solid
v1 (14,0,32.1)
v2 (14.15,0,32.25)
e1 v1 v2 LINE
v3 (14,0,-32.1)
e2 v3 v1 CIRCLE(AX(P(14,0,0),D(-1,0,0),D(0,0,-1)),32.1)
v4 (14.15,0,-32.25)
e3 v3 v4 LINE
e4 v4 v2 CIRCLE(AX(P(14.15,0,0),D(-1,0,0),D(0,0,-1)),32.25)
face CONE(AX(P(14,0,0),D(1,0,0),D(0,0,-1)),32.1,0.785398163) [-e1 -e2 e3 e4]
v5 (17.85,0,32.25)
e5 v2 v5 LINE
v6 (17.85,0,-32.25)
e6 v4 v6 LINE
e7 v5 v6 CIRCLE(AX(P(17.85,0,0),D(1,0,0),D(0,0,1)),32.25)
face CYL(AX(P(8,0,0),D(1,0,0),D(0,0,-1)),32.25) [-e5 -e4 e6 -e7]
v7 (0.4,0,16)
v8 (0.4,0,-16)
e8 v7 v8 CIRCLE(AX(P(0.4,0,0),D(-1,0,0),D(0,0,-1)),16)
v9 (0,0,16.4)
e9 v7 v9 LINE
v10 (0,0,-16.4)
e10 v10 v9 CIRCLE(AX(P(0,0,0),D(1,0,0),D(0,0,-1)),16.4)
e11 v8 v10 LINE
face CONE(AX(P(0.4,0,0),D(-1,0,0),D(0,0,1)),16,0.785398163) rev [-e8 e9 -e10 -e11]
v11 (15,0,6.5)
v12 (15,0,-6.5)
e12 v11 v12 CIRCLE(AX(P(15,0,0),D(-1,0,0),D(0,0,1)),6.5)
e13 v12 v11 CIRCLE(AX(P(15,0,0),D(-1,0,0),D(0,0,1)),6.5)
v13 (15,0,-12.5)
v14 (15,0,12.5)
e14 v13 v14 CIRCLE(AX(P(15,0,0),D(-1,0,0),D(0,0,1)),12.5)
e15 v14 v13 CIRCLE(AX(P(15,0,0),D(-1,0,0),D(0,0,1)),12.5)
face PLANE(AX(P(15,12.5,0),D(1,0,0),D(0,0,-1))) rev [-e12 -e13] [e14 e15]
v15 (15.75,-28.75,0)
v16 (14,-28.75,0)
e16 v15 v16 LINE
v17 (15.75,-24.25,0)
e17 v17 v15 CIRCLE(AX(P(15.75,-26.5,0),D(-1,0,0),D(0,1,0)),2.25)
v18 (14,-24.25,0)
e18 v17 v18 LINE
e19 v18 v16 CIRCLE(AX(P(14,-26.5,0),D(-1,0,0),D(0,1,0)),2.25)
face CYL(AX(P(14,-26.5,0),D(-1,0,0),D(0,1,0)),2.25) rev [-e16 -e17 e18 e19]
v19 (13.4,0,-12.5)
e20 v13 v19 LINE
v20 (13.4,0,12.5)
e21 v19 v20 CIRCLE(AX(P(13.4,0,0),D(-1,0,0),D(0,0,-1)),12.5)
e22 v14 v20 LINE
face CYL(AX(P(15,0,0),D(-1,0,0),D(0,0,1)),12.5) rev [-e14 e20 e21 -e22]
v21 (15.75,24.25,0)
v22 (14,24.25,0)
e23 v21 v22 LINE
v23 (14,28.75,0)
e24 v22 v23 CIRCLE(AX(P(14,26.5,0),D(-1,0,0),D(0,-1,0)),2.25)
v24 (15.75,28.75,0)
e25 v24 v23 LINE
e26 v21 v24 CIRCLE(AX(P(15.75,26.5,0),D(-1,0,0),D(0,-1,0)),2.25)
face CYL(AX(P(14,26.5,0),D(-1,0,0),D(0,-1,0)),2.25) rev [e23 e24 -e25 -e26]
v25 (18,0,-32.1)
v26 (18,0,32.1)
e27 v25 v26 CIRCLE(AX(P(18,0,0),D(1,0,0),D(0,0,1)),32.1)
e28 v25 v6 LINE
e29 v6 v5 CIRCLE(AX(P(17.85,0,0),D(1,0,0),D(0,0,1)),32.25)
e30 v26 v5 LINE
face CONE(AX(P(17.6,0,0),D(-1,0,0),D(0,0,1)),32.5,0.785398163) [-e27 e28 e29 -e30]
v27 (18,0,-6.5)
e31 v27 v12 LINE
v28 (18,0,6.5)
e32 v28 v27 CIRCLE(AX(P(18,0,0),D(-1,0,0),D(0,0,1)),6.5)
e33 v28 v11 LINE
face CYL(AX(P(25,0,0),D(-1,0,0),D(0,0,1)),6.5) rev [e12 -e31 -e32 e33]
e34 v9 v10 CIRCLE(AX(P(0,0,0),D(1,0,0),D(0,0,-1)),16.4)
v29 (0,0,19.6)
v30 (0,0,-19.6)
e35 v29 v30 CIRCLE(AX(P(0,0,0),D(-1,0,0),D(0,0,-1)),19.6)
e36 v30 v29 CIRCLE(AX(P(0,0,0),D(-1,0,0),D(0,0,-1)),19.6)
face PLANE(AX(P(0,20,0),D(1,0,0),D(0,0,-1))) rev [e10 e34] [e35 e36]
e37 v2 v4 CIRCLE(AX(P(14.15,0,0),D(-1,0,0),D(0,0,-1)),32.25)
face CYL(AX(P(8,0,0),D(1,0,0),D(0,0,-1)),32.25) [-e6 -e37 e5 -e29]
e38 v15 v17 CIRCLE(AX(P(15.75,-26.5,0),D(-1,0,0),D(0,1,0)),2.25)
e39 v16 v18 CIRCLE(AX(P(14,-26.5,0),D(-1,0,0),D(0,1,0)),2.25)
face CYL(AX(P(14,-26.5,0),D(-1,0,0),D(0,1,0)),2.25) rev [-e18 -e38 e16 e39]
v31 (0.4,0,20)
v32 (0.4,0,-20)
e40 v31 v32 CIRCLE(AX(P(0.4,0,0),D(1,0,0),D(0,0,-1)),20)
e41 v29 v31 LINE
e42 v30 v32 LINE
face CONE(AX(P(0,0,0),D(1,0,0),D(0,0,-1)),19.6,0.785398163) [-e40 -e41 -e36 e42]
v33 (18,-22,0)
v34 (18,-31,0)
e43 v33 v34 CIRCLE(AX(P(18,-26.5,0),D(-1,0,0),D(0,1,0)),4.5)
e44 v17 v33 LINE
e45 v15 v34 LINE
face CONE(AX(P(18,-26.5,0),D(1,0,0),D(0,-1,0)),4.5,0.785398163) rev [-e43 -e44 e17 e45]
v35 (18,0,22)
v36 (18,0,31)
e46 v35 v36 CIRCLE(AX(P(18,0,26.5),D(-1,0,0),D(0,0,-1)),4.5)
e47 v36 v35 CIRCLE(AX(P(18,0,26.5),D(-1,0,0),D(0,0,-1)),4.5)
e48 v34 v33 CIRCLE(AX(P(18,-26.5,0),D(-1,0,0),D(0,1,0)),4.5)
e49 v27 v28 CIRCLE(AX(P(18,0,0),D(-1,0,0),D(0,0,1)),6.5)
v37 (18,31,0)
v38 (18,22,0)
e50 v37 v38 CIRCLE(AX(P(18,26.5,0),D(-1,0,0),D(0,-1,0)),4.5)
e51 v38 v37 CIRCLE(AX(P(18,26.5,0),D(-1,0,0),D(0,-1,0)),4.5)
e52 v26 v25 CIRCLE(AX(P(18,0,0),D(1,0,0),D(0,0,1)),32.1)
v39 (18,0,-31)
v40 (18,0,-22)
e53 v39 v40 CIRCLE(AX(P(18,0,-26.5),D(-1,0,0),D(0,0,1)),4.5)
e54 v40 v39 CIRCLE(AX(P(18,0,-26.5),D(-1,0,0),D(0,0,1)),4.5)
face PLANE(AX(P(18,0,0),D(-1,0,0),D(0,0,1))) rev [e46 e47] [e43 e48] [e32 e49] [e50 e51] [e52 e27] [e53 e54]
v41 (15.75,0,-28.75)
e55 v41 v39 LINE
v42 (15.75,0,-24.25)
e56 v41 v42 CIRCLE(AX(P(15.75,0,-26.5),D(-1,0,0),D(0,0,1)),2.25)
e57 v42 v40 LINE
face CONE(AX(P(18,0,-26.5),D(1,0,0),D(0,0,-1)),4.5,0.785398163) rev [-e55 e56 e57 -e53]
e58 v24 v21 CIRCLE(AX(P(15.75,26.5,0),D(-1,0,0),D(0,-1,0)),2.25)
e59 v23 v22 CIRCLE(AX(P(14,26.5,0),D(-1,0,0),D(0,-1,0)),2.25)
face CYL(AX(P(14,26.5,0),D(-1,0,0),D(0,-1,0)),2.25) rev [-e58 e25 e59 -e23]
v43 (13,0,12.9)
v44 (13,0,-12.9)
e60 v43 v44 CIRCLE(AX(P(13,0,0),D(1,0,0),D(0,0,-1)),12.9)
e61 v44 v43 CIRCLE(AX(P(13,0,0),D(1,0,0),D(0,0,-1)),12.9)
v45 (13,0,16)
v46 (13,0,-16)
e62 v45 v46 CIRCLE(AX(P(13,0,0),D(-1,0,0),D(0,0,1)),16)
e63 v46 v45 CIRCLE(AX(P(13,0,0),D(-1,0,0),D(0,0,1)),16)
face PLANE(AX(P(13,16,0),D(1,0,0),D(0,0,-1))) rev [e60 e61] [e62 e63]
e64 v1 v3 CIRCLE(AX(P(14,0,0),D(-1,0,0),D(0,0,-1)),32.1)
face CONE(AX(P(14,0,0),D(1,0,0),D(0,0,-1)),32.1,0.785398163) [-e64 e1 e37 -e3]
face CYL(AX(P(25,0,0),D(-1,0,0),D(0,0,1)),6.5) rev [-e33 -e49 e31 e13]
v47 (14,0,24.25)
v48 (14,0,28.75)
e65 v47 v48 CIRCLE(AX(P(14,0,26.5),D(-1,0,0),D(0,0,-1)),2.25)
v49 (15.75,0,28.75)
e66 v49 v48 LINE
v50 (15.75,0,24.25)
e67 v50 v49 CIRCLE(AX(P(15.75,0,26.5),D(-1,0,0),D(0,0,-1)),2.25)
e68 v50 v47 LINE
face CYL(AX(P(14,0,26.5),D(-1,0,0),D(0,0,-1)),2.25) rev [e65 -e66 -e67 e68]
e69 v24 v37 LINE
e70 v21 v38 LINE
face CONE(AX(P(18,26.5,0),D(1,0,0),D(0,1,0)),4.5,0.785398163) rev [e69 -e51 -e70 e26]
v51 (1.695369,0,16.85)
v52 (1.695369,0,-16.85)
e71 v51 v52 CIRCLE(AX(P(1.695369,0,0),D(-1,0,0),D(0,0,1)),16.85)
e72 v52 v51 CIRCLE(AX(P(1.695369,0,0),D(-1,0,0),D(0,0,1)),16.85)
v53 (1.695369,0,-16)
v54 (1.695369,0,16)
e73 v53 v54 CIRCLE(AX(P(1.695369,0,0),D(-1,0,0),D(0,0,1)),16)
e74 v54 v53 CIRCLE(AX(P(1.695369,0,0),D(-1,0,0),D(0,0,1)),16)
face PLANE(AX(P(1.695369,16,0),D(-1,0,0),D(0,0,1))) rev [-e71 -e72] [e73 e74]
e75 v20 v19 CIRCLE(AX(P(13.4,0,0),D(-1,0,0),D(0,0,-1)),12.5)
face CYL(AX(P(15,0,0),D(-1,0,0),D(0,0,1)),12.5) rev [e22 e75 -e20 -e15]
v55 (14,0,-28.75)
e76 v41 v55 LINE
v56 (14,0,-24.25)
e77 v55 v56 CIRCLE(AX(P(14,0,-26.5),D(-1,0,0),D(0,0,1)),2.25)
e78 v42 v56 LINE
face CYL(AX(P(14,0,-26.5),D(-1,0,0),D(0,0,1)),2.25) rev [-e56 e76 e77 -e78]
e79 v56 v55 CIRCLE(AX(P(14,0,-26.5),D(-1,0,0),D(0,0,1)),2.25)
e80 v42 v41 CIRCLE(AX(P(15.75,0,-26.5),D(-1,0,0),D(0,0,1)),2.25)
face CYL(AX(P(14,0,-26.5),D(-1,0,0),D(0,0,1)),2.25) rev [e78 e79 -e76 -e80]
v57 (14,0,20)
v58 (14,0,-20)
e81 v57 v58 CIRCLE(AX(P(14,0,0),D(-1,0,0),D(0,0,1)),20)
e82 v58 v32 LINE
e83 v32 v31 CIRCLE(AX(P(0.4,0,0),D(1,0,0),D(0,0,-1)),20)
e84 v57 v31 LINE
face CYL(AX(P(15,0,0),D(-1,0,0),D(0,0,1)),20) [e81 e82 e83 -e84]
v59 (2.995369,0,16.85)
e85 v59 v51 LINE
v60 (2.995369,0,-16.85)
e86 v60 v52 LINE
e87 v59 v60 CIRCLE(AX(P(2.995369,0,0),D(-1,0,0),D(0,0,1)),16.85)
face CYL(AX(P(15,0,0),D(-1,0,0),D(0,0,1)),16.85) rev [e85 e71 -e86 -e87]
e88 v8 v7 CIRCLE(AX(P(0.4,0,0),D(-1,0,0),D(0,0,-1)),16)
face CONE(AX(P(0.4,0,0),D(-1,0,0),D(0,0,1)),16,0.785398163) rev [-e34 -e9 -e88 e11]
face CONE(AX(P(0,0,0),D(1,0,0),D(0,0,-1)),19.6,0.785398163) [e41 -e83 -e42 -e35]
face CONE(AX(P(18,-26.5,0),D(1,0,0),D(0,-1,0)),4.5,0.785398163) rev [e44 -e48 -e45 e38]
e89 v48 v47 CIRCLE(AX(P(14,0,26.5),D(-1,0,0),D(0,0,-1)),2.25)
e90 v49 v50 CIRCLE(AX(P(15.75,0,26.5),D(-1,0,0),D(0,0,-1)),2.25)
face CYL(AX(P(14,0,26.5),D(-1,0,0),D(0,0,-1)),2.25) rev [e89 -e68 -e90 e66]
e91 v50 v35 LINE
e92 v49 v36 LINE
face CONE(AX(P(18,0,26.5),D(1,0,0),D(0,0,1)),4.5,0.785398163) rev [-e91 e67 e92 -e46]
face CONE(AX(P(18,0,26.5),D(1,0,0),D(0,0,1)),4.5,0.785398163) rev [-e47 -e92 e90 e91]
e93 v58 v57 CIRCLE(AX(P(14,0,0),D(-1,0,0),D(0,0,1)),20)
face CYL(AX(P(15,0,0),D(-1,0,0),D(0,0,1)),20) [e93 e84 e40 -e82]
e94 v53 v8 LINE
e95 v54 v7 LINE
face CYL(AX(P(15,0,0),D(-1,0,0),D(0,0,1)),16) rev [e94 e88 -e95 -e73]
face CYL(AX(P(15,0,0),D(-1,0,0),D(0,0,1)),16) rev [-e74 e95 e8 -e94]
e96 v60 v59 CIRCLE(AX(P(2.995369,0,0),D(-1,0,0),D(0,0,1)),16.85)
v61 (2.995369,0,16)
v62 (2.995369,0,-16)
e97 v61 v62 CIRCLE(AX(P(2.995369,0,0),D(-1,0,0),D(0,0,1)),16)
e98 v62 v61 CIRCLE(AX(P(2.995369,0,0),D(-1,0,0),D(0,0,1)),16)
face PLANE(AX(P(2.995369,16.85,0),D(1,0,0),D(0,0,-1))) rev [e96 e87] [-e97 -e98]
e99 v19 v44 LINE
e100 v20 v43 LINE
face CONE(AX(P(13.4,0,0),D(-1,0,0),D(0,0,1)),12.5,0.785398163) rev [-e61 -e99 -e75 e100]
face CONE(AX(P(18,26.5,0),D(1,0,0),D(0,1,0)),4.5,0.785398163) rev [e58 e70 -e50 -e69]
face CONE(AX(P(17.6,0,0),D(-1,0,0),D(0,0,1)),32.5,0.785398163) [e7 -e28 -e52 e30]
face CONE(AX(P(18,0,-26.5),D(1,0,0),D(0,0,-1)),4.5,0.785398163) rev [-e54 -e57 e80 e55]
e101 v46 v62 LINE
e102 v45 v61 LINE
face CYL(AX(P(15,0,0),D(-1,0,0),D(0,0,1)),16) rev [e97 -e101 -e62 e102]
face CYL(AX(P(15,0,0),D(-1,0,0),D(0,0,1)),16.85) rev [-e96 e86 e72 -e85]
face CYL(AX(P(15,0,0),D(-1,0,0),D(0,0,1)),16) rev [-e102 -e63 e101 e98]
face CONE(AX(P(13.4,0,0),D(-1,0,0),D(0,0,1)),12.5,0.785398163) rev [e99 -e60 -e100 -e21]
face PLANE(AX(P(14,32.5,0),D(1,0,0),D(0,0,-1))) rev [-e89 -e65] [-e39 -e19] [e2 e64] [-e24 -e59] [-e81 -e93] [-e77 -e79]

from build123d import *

# Parameters (mm, degrees)
CIRPATTERN1_COUNT  = 4
CHAMFER1_SIZE      = 0.4
SKETCH8_R          = 6.5
CUT_EXTRUDE1_DEPTH = 10
SKETCH9_R          = 33
SKETCH9_R_2        = 32.25
CUT_EXTRUDE2_DEPTH = 10


with BuildPart() as part:
    # Sketch1 → Revolve1 (revolve)
    with BuildSketch(Plane.XY, mode=Mode.PRIVATE) as revolve1_sk:
        Polygon((0, 16), (1.695369244, 16), (1.695369244, 16.85), (2.995369244, 16.85), (2.995369244, 16), (13, 16), (13, 12.5), (15, 12.5), (15, 0), (18, 0), (18, 32.5), (14, 32.5), (14, 20), (0, 20), align=None)
    revolve(revolve1_sk.sketch.rotate(Axis((15, 0, 0), (1, 0, 0)), 90), axis=Axis((15, 0, 0), (1, 0, 0)))

    # Sketch2 → Cut-Revolve1 (revolve, cut)
    with BuildSketch(Plane(origin=(0, 0, 0), x_dir=(1, 0, 0), z_dir=(0, 1, 0)), mode=Mode.PRIVATE) as cut_revolve1_sk:
        Polygon((14, 26.5), (18, 26.5), (18, 31), (15.75, 28.75), (14, 28.75), align=None)
    cut_revolve1 = revolve(cut_revolve1_sk.sketch.rotate(Axis((14, 0, -26.5), (1, 0, 0)), 180), axis=Axis((14, 0, -26.5), (1, 0, 0)), mode=Mode.SUBTRACT)

    # CirPattern1: Cut-Revolve1 ×4 about axis
    cirpattern1_axis = Axis((0, 0, 0), (1, 0, 0))
    for i in range(1, CIRPATTERN1_COUNT):
        add(cut_revolve1.rotate(cirpattern1_axis, i * 360 / CIRPATTERN1_COUNT), mode=Mode.SUBTRACT)

    # Chamfer1
    chamfer1_edges = [part.edges().sort_by_distance(p)[0] for p in [
        (14, 0, -32.5),
        (18, 0, -32.5),
        (13, 0, -12.5),
        (0, 0, -16),
        (0, 0, -20),
    ]]
    chamfer(chamfer1_edges, length=CHAMFER1_SIZE)

    # Sketch8 → Cut-Extrude1 (cut)
    with BuildSketch(Plane.ZY.offset(-15)):
        Circle(SKETCH8_R)
    extrude(amount=-CUT_EXTRUDE1_DEPTH, mode=Mode.SUBTRACT)

    # Sketch9 → Cut-Extrude2 (cut)
    with BuildSketch(Plane(origin=(18, 0, 0), x_dir=(0, 0, -1), z_dir=(1, 0, 0))):
        Circle(SKETCH9_R)
        Circle(SKETCH9_R_2, mode=Mode.SUBTRACT)
    extrude(amount=-CUT_EXTRUDE2_DEPTH, mode=Mode.SUBTRACT)


solid = part.part
